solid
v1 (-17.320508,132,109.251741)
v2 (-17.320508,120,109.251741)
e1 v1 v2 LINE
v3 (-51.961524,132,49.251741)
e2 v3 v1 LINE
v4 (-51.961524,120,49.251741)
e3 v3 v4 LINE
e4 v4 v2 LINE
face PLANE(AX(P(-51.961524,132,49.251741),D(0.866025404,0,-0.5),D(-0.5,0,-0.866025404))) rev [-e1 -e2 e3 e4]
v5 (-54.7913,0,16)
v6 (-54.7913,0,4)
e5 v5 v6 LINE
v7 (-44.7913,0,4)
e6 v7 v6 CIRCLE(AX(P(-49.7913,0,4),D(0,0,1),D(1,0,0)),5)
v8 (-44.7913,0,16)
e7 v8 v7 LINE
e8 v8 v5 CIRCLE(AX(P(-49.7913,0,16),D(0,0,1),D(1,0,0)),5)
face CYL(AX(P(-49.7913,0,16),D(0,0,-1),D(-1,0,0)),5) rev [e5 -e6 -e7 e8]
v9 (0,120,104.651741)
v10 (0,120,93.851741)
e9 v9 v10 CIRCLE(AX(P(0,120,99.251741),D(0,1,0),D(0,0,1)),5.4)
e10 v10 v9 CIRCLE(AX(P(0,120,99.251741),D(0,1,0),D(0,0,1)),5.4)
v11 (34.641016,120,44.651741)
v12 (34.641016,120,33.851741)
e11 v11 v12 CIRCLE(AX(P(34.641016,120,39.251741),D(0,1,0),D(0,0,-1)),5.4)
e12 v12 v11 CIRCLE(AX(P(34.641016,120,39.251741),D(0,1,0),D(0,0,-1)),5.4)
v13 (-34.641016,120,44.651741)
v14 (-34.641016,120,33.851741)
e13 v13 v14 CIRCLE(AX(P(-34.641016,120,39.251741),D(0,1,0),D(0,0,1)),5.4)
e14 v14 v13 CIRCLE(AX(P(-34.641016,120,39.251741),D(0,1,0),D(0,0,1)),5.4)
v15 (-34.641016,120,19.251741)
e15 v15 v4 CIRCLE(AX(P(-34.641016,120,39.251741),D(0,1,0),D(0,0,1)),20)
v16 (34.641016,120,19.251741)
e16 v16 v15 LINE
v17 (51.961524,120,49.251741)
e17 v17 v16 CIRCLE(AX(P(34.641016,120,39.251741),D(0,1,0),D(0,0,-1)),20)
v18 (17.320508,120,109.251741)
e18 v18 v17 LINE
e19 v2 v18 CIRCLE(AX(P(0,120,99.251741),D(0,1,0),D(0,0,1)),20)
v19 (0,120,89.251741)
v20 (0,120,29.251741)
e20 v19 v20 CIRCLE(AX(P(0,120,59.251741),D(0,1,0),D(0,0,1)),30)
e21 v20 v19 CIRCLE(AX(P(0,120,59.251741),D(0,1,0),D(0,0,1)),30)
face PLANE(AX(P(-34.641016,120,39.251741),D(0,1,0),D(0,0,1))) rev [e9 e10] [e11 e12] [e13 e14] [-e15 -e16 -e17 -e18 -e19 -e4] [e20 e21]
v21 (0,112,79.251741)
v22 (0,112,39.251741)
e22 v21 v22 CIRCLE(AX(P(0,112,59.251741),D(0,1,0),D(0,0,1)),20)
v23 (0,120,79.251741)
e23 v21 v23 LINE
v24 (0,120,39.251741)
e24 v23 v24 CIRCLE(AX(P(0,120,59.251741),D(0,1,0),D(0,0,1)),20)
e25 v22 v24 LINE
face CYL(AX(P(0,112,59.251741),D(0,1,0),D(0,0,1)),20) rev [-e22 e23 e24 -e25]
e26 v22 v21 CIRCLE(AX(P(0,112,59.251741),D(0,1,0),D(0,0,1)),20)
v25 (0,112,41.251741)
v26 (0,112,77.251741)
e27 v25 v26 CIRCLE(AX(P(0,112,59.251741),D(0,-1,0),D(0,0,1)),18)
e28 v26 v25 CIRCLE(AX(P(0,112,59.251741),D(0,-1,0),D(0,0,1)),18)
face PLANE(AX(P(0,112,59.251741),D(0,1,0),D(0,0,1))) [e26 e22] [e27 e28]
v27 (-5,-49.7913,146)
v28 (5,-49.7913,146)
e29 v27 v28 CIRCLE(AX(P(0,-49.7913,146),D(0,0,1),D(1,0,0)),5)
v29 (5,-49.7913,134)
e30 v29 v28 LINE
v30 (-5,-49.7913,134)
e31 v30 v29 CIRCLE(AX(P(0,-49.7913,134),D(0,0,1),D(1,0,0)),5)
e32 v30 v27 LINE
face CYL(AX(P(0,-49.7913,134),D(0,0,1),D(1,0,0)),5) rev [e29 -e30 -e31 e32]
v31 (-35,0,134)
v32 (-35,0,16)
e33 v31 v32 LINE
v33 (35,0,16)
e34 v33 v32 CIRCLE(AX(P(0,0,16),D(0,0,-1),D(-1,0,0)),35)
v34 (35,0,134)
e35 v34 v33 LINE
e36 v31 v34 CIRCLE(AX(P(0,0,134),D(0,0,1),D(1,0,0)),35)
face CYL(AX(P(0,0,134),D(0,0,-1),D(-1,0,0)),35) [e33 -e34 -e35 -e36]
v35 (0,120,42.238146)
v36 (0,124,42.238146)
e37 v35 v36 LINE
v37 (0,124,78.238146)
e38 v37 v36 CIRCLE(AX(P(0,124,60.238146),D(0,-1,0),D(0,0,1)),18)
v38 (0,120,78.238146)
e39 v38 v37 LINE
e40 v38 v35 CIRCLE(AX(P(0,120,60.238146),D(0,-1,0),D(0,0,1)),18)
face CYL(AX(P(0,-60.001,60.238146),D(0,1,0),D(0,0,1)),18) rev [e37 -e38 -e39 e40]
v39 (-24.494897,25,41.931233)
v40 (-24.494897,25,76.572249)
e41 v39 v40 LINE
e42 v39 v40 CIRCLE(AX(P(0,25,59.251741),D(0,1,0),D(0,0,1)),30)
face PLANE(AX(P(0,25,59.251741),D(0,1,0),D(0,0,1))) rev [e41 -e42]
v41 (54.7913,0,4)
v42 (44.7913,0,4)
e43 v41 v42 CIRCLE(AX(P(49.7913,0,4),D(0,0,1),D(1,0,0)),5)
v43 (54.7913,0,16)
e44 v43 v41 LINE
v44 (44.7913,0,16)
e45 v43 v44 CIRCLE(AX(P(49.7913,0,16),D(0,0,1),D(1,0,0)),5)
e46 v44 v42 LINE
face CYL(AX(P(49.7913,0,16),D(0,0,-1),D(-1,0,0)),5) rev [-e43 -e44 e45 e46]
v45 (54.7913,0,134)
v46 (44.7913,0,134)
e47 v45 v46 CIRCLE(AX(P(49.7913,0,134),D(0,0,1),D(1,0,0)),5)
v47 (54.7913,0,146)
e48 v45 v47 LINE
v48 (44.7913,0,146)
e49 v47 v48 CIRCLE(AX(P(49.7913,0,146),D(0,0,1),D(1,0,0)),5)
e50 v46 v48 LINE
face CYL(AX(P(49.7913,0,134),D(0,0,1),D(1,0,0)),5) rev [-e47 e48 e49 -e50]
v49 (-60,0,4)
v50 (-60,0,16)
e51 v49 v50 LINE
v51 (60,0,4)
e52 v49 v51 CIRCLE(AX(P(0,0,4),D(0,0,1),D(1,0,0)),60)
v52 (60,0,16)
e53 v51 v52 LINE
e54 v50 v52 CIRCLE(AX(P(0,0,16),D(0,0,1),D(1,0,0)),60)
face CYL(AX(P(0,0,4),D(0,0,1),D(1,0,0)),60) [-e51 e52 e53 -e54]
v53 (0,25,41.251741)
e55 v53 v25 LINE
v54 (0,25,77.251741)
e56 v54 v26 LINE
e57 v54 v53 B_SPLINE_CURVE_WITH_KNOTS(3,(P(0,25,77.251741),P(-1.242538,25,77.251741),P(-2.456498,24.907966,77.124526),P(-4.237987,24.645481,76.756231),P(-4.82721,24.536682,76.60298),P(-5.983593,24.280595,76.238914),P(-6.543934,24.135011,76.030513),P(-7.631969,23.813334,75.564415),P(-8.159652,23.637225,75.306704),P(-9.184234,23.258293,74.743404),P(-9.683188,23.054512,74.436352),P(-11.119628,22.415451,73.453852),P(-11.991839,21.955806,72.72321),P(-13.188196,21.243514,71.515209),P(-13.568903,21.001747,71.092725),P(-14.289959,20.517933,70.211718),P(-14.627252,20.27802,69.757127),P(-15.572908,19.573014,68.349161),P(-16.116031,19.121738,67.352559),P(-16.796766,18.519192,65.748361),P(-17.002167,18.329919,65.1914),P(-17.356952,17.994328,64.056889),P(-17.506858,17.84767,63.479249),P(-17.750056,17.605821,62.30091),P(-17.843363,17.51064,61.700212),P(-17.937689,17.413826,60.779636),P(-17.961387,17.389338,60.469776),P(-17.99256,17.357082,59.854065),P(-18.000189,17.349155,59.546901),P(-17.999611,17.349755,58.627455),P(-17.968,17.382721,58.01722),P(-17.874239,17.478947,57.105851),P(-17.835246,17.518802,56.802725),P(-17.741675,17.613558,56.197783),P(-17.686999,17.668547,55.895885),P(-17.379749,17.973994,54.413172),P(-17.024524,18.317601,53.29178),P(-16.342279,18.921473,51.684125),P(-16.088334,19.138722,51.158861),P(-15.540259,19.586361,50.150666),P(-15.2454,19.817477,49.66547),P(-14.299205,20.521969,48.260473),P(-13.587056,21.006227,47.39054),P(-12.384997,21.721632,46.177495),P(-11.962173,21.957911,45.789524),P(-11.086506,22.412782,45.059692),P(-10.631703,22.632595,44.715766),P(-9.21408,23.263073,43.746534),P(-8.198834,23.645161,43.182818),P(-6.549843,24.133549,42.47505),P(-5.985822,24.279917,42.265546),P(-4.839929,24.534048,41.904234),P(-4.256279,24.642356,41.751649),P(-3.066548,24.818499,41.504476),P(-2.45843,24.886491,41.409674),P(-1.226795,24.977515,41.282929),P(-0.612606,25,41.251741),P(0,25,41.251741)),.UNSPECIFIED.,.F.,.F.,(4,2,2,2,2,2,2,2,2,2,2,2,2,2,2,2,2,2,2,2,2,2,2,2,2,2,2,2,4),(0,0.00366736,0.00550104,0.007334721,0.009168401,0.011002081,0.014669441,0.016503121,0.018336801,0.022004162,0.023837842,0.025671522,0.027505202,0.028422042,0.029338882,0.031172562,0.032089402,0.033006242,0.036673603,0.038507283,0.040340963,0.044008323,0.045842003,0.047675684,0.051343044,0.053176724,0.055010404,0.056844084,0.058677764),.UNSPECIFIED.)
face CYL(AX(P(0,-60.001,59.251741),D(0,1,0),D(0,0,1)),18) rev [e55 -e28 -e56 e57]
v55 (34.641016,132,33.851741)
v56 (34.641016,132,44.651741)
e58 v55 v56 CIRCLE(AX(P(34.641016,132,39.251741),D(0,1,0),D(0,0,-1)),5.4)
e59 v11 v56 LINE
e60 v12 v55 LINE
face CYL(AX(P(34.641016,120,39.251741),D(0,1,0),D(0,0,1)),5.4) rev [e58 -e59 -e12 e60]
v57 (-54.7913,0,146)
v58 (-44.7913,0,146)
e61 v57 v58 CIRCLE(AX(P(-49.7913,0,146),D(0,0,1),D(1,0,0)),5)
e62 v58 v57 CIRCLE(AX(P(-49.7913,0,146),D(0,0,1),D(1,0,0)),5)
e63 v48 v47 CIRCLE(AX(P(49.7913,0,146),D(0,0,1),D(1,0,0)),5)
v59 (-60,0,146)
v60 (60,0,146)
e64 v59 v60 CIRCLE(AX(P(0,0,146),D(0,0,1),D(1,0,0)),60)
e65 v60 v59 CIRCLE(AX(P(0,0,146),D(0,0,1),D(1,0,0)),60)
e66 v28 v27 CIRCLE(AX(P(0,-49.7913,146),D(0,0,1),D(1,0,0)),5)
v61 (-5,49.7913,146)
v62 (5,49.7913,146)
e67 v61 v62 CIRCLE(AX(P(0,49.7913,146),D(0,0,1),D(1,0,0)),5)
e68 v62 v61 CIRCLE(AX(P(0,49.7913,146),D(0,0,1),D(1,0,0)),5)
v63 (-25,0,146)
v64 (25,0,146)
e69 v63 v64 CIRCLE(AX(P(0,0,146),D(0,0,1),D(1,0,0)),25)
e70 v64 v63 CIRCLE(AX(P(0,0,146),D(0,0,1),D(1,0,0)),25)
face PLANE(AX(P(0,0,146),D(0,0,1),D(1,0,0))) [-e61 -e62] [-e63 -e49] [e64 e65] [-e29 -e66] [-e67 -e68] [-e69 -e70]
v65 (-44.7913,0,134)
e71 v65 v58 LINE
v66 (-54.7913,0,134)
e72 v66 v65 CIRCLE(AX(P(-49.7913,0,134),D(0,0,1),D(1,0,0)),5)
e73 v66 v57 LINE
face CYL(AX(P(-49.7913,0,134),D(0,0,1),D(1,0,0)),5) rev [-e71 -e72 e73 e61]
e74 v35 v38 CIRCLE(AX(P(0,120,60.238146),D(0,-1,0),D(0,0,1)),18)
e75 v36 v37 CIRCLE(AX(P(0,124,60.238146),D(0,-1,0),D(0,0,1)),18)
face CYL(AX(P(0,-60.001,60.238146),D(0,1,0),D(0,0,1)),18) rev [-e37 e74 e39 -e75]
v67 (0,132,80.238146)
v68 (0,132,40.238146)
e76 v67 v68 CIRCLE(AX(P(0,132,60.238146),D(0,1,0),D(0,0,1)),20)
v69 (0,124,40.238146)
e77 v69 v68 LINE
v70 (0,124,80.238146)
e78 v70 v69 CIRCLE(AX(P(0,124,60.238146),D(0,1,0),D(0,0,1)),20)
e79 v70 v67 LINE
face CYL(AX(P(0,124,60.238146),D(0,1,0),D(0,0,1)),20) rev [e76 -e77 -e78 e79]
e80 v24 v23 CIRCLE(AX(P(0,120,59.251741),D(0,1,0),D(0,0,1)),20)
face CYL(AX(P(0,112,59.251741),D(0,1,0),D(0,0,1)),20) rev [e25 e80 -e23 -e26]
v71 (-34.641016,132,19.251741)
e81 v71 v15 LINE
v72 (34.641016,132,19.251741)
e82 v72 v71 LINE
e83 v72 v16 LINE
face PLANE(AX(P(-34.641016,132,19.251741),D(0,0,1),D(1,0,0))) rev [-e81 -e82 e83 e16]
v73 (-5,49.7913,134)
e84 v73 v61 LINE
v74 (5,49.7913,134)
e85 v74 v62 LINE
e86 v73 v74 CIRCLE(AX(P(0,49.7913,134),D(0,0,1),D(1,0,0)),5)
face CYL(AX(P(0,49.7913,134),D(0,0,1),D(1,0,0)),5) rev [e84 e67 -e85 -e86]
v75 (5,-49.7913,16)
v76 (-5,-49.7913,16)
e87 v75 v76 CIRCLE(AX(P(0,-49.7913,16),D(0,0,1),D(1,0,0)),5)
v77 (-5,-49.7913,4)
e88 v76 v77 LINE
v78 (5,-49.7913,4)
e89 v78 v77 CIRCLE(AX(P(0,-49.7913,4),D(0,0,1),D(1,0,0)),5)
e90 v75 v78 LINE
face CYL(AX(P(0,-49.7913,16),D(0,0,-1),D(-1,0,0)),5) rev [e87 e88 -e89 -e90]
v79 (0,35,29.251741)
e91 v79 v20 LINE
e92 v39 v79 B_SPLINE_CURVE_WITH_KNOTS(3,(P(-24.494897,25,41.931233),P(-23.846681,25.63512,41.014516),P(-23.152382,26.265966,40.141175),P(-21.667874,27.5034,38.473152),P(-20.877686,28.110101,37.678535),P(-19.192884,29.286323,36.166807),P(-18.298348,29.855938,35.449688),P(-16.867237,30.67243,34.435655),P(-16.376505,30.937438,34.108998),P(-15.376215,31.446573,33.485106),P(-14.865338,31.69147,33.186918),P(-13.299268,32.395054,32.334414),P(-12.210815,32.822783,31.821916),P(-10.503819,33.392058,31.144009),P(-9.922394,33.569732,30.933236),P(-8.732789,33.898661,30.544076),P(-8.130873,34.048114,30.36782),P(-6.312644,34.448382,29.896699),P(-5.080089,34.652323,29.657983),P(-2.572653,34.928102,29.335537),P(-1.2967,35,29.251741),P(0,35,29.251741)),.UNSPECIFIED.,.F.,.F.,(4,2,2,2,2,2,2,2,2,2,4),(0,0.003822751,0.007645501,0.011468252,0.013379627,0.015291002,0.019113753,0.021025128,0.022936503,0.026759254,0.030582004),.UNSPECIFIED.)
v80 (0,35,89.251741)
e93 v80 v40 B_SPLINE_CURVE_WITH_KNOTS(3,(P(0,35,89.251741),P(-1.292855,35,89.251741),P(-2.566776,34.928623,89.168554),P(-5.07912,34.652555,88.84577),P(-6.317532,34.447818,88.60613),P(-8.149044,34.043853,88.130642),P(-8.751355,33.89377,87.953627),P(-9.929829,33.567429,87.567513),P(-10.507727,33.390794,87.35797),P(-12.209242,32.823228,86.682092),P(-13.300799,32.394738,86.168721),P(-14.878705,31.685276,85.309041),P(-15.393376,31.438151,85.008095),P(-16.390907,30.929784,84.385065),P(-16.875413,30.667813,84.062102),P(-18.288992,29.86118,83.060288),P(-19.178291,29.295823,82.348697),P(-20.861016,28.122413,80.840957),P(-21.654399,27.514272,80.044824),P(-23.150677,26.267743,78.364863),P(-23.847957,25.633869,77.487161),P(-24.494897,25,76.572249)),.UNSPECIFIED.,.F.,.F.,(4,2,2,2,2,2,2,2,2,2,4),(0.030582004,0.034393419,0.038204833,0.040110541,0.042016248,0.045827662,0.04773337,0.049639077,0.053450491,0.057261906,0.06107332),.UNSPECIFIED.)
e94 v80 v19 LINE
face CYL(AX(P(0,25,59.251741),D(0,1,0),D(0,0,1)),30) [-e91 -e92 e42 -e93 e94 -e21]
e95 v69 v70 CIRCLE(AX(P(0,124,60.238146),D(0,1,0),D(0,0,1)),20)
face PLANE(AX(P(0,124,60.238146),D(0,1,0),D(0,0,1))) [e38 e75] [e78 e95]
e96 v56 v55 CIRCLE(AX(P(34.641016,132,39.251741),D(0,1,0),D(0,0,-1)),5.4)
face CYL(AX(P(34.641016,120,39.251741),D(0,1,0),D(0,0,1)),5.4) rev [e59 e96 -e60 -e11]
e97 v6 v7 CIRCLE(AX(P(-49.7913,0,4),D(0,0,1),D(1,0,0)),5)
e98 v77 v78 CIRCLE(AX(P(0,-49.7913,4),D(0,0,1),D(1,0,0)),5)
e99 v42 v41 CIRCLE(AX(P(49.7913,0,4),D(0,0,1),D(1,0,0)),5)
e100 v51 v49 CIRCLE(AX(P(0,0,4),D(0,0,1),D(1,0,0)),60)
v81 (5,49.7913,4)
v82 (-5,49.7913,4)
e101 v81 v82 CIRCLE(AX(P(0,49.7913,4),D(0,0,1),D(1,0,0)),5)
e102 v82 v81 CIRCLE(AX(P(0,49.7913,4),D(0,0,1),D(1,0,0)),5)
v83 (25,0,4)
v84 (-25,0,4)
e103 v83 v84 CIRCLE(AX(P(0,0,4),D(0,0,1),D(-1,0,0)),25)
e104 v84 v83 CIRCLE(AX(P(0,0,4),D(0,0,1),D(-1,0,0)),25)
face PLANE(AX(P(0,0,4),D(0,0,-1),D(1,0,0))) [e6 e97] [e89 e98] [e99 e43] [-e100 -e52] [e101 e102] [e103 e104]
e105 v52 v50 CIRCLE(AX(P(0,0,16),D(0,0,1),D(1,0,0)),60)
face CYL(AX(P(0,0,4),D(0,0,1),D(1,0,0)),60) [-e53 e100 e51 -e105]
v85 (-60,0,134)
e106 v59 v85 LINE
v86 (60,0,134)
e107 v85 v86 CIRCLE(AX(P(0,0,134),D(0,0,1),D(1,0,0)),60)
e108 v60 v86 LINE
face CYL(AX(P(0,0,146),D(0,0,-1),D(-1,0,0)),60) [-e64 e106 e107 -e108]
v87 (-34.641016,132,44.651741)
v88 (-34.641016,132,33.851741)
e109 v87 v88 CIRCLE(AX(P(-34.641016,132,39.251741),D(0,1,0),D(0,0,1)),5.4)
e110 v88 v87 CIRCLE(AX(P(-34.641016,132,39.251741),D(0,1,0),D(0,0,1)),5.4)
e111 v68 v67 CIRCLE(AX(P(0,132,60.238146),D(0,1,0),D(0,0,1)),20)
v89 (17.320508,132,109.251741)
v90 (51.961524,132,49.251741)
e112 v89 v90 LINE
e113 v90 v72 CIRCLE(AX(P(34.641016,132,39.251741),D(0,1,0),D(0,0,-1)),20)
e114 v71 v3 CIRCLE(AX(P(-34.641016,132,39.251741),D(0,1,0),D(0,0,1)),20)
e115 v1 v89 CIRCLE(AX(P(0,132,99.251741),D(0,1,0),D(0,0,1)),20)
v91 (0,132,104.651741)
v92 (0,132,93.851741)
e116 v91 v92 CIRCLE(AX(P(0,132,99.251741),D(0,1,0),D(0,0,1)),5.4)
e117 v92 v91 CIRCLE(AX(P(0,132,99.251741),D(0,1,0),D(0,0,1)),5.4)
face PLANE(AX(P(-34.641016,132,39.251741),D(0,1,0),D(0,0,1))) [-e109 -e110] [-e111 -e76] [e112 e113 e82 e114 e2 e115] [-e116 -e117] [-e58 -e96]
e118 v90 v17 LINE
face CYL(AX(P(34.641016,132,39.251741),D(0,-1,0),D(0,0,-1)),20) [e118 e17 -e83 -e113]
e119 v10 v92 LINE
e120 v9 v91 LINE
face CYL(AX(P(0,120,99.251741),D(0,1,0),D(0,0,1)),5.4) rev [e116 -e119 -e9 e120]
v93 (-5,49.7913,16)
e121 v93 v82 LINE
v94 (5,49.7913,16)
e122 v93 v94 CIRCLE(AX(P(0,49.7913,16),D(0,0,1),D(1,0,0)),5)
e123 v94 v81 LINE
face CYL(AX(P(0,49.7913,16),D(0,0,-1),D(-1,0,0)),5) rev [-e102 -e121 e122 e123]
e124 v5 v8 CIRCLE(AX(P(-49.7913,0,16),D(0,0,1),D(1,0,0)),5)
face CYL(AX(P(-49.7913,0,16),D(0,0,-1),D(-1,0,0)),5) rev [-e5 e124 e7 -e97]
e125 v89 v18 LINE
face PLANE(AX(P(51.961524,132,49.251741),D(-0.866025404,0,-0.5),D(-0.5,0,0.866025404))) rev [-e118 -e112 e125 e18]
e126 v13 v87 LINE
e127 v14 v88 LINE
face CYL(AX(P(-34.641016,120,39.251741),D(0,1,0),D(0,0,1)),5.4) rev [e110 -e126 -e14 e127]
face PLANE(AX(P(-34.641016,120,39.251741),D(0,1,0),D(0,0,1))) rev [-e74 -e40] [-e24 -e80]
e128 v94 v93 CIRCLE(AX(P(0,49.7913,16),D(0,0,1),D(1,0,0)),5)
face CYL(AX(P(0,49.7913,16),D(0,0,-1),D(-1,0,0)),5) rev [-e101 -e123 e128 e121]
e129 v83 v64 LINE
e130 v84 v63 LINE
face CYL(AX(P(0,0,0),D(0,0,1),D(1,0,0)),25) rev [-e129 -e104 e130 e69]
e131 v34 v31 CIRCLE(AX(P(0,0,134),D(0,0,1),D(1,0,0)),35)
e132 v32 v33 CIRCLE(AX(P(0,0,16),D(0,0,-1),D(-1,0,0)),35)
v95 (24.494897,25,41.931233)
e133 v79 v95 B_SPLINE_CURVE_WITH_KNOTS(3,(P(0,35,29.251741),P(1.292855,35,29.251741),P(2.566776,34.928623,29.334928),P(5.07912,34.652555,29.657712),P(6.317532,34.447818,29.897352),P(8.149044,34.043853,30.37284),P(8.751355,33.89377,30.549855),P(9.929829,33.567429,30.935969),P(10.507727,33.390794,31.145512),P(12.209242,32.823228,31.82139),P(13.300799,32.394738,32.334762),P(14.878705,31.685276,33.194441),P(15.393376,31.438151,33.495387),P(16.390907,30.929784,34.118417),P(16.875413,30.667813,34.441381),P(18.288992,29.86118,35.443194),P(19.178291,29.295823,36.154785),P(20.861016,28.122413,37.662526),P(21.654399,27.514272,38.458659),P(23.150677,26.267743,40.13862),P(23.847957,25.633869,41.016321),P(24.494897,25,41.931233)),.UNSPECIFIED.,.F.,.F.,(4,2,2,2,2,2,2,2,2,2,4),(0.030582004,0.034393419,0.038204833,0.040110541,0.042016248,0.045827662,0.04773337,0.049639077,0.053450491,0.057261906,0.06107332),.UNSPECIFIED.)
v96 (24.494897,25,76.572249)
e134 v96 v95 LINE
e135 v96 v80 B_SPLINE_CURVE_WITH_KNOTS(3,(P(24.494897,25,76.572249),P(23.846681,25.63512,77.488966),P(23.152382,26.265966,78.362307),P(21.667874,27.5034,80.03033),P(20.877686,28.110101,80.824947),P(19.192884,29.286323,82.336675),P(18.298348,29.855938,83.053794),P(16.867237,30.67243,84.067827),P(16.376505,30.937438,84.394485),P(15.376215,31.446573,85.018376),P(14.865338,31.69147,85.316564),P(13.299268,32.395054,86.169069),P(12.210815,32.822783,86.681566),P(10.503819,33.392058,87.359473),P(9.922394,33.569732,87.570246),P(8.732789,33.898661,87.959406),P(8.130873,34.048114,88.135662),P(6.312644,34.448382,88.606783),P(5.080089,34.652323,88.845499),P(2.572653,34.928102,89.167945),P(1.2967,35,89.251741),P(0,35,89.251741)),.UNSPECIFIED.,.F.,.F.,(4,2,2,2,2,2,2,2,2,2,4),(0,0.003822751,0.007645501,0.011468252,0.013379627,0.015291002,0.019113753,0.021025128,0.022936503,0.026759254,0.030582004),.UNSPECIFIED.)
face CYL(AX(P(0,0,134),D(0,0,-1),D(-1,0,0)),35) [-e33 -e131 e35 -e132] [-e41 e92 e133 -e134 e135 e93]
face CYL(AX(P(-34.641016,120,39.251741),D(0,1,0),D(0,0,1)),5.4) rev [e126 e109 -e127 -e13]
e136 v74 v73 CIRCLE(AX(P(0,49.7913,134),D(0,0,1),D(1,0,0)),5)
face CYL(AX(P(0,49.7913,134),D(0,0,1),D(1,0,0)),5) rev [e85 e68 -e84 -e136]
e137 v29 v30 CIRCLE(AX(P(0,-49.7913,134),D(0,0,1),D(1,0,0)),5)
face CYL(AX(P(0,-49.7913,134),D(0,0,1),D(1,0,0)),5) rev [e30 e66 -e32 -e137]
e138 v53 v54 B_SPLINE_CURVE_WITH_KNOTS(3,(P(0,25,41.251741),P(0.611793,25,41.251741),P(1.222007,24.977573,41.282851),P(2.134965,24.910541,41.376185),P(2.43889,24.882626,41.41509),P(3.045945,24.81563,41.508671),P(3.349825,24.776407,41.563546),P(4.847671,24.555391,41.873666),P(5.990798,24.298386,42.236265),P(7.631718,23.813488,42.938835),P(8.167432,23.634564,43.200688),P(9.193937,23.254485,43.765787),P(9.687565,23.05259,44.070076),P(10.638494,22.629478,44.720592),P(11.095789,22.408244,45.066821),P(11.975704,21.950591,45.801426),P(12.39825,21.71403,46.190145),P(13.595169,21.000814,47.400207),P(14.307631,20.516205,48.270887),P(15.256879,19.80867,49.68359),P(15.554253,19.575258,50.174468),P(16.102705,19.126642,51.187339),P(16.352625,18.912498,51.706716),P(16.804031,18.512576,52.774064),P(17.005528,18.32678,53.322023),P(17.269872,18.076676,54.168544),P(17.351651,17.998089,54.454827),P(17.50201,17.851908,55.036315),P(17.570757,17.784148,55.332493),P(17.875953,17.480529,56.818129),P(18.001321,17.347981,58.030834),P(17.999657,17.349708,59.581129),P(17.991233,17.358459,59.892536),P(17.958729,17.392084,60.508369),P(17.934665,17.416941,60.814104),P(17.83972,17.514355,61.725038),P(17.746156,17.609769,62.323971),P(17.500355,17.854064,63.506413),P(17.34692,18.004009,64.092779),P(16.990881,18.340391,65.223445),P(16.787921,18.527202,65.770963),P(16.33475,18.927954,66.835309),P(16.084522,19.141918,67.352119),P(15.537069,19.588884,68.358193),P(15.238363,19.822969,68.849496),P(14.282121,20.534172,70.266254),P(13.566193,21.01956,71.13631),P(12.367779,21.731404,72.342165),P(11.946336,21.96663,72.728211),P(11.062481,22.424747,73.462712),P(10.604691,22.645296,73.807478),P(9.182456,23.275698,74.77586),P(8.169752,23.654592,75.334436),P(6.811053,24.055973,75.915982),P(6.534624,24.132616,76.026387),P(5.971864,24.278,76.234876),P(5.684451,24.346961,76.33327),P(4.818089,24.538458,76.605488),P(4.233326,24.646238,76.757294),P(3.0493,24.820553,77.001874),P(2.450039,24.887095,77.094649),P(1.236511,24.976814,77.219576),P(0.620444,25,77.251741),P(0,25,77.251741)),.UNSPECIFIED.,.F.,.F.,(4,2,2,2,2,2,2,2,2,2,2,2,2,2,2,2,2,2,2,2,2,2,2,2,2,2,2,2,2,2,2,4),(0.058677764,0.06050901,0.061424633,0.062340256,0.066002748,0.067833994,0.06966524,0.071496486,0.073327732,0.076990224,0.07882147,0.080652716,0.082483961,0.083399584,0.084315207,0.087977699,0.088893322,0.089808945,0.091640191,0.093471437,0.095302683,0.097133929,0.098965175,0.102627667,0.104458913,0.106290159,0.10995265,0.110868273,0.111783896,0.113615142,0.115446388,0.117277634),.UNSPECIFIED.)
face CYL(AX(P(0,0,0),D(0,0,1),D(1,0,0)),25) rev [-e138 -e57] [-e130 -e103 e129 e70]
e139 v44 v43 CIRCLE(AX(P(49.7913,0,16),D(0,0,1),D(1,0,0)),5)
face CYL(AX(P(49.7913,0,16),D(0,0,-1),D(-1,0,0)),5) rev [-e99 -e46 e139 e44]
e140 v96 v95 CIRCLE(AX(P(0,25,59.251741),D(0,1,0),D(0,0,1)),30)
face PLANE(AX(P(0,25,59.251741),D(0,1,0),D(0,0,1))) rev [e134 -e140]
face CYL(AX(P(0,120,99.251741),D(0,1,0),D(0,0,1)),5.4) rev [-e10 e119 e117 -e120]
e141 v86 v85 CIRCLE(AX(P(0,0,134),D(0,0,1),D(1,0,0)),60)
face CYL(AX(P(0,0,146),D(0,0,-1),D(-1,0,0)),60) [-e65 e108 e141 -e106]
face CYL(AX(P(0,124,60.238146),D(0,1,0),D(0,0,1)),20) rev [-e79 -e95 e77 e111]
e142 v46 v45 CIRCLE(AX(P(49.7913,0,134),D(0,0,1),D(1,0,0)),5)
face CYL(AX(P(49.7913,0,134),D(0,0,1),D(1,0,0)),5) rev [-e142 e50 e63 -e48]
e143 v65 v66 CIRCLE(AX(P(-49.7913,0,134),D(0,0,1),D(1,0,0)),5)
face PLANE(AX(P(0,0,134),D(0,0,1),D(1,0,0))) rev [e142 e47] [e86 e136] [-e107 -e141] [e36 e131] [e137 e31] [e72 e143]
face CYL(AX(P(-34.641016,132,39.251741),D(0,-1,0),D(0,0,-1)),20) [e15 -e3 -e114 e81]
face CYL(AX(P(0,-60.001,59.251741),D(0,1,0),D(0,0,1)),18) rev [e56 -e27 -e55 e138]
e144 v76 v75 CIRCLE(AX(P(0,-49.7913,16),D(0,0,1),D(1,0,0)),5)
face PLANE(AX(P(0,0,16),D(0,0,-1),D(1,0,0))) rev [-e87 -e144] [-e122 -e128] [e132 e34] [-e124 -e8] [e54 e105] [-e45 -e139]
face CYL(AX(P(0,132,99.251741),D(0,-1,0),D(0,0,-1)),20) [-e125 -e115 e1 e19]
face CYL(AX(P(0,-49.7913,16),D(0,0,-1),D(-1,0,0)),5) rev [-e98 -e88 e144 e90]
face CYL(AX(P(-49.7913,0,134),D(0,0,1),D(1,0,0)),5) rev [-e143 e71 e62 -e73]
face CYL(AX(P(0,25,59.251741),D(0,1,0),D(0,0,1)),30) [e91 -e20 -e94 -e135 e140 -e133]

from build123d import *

# Parameters (mm, degrees)
MAIN_PIPE_SKETCH_R                   = 35
MAIN_PIPE_70X134_DEPTH               = 134
MAIN_BORE_SKETCH_R                   = 25
MAIN_BORE_50_DEPTH                   = 134
END_FLANGE_SKETCH_R                  = 60
END_FLANGE_120X12_DEPTH              = 12
END_FLANGE_BOLT_HOLES_SKETCH_R       = 5
END_FLANGE_BOLT_HOLES_4X_10_DEPTH    = 12
END_FLANGE_BORE_SKETCH_R             = 25
END_FLANGE_BORE_50_DEPTH             = 169.866811422
OPPOSITE_FLANGE_BORE_SKETCH_R        = 25
OPPOSITE_FLANGE_BORE_DEPTH           = 166.420675854
END_FACE_CUT_SKETCH_R                = 35
END_FACE_CUT_4MM_DEPTH               = 4
BRANCH_PIPE_SKETCH_R                 = 30
BRANCH_PIPE_60_DEPTH                 = 95
BRANCH_BORE_36_REACH                 = 241.408
BRANCH_BORE_36_END_RADIUS            = 25
BRANCH_BORE_SKETCH_R                 = 18
BRANCH_COUNTERBORE_SKETCH_R          = 20
BRANCH_COUNTERBORE_40X8_DEPTH        = 8
TRIANGULAR_BRANCH_FLANGE_DEPTH       = 12
BRANCH_FLANGE_HOLES_SKETCH_R         = 5.4
BRANCH_FLANGE_BOLT_HOLES_DEPTH       = 12
BRANCH_FLANGE_BORE_36_REACH          = 250.556
BRANCH_FLANGE_BORE_SKETCH_R          = 18
BRANCH_FLANGE_COUNTERBORE_SKETCH_R   = 20
BRANCH_FLANGE_COUNTERBORE_40X8_DEPTH = 8


with BuildPart() as part:
    # Main Pipe Sketch → Main Pipe Ø70x134 (new body)
    with BuildSketch(Plane.XY):
        Circle(MAIN_PIPE_SKETCH_R)
    extrude(amount=MAIN_PIPE_70X134_DEPTH)

    # Main Bore Sketch → Main Bore Ø50 (cut)
    with BuildSketch(Plane.XY.offset(134)):
        Circle(MAIN_BORE_SKETCH_R)
    extrude(amount=-MAIN_BORE_50_DEPTH, mode=Mode.SUBTRACT)

    # End Flange Sketch → End Flange Ø120x12 (add)
    with BuildSketch(Plane.XY.offset(134)):
        Circle(END_FLANGE_SKETCH_R)
    end_flange_120x12 = extrude(amount=END_FLANGE_120X12_DEPTH)

    # End Flange Bolt Holes Sketch → End Flange Bolt Holes 4xØ10 (cut)
    with BuildSketch(Plane.XY.offset(146)):
        with Locations((0, 49.791299633)):
            Circle(END_FLANGE_BOLT_HOLES_SKETCH_R)
        with Locations((49.791299633, 0)):
            Circle(END_FLANGE_BOLT_HOLES_SKETCH_R)
        with Locations((0, -49.791299633)):
            Circle(END_FLANGE_BOLT_HOLES_SKETCH_R)
        with Locations((-49.791299633, 0)):
            Circle(END_FLANGE_BOLT_HOLES_SKETCH_R)
    end_flange_bolt_holes_4x_10 = extrude(amount=-END_FLANGE_BOLT_HOLES_4X_10_DEPTH, mode=Mode.SUBTRACT)

    # End Flange Bore Sketch → End Flange Bore Ø50 (cut, through all)
    with BuildSketch(Plane.XY.offset(146)):
        Circle(END_FLANGE_BORE_SKETCH_R)
    extrude(amount=-END_FLANGE_BORE_50_DEPTH, mode=Mode.SUBTRACT)

    # Opposite End Flange Mirror: End Flange Ø120x12, End Flange Bolt Holes 4xØ10 across plane
    add(end_flange_120x12.mirror(Plane.XY.offset(75)))
    add(end_flange_bolt_holes_4x_10.mirror(Plane.XY.offset(75)), mode=Mode.SUBTRACT)

    # Opposite Flange Bore Sketch → Opposite Flange Bore (cut, through all)
    with BuildSketch(Plane(origin=(0, 0, 4), x_dir=(-1, 0, 0), z_dir=(0, 0, -1))):
        with Locations(Location((0, 0, 0), (0, 0, 180))):
            Circle(OPPOSITE_FLANGE_BORE_SKETCH_R)
    extrude(amount=-OPPOSITE_FLANGE_BORE_DEPTH, mode=Mode.SUBTRACT)

    # End Face Cut Sketch → End Face Cut 4mm (cut)
    with BuildSketch(Plane(origin=(0, 0, 0), x_dir=(-1, 0, 0), z_dir=(0, 0, -1))):
        Circle(END_FACE_CUT_SKETCH_R)
    extrude(amount=-END_FACE_CUT_4MM_DEPTH, mode=Mode.SUBTRACT)

    # Branch Pipe Sketch → Branch Pipe Ø60 (add)
    with BuildSketch(Plane(origin=(0, 120, 0), x_dir=(1, 0, 0), z_dir=(0, 1, 0))):
        with Locations(Location((0, -59.251741082, 0), (0, 0, 270))):
            Circle(BRANCH_PIPE_SKETCH_R)
    extrude(amount=-BRANCH_PIPE_60_DEPTH)

    # Branch Bore Ø36: up to this cylinder (the profile starts outside it)
    branch_bore_36_end = Plane(origin=(0, 0, 59.251741), z_dir=(0, 0, 1)) * Cylinder(BRANCH_BORE_36_END_RADIUS, 533.816, mode=Mode.PRIVATE)
    # Branch Bore Sketch → Branch Bore Ø36 (cut, up to the surface)
    with BuildSketch(Plane(origin=(0, 120, 0), x_dir=(1, 0, 0), z_dir=(0, 1, 0)), mode=Mode.PRIVATE) as branch_bore_36_sk1:
        with Locations(Location((0, -59.251741082, 0), (0, 0, 270))):
            Circle(BRANCH_BORE_SKETCH_R)
    branch_bore_36_tool1 = extrude(branch_bore_36_sk1.sketch, amount=-BRANCH_BORE_36_REACH, mode=Mode.PRIVATE) - branch_bore_36_end
    add(branch_bore_36_tool1.solids().sort_by_distance((0, 120, 59.251741))[0], mode=Mode.SUBTRACT)

    # Branch Counterbore Sketch → Branch Counterbore Ø40x8 (cut)
    with BuildSketch(Plane(origin=(0, 120, 0), x_dir=(1, 0, 0), z_dir=(0, 1, 0))):
        with Locations(Location((0, -59.251741082, 0), (0, 0, 270))):
            Circle(BRANCH_COUNTERBORE_SKETCH_R)
    extrude(amount=-BRANCH_COUNTERBORE_40X8_DEPTH, mode=Mode.SUBTRACT)

    # Branch Flange Sketch → Triangular Branch Flange (add)
    with BuildSketch(Plane(origin=(0, 120, 0), x_dir=(1, 0, 0), z_dir=(0, 1, 0))):
        with BuildLine():
            Line((-51.961524227, -49.251741082), (-17.320508076, -109.251741082))
            ThreePointArc((-17.320508076, -109.251741082), (0, -119.251741082), (17.320508076, -109.251741082))
            Line((17.320508076, -109.251741082), (51.961524227, -49.251741082))
            ThreePointArc((51.961524227, -49.251741082), (51.961524227, -29.251741082), (34.641016151, -19.251741082))
            Line((34.641016151, -19.251741082), (-34.641016151, -19.251741082))
            ThreePointArc((-34.641016151, -19.251741082), (-51.961524227, -29.251741082), (-51.961524227, -49.251741082))
        make_face()
    extrude(amount=TRIANGULAR_BRANCH_FLANGE_DEPTH)

    # Branch Flange Holes Sketch → Branch Flange Bolt Holes (cut)
    with BuildSketch(Plane(origin=(0, 132, 0), x_dir=(1, 0, 0), z_dir=(0, 1, 0))):
        with Locations(Location((-34.641016151, -39.251741082, 0), (0, 0, 270))):
            Circle(BRANCH_FLANGE_HOLES_SKETCH_R)
        with Locations(Location((34.641016151, -39.251741082, 0), (0, 0, 90))):
            Circle(BRANCH_FLANGE_HOLES_SKETCH_R)
        with Locations(Location((0, -99.251741082, 0), (0, 0, 270))):
            Circle(BRANCH_FLANGE_HOLES_SKETCH_R)
    extrude(amount=-BRANCH_FLANGE_BOLT_HOLES_DEPTH, mode=Mode.SUBTRACT)

    # Branch Flange Bore Sketch → Branch Flange Bore Ø36 (cut, up to next)
    with BuildSketch(Plane(origin=(0, 132, 0), x_dir=(1, 0, 0), z_dir=(0, 1, 0)), mode=Mode.PRIVATE) as branch_flange_bore_36_sk1:
        with Locations(Location((0, -60.238145752, 0), (0, 0, 270))):
            Circle(BRANCH_FLANGE_BORE_SKETCH_R)
    branch_flange_bore_36_tool1 = extrude(branch_flange_bore_36_sk1.sketch, amount=-BRANCH_FLANGE_BORE_36_REACH, mode=Mode.PRIVATE) & part.part
    add(branch_flange_bore_36_tool1.solids().sort_by_distance((0, 132, 60.238146))[0], mode=Mode.SUBTRACT)

    # Branch Flange Counterbore Sketch → Branch Flange Counterbore Ø40x8 (cut)
    with BuildSketch(Plane(origin=(0, 132, 0), x_dir=(1, 0, 0), z_dir=(0, 1, 0))):
        with Locations(Location((0, -60.238145752, 0), (0, 0, 270))):
            Circle(BRANCH_FLANGE_COUNTERBORE_SKETCH_R)
    extrude(amount=-BRANCH_FLANGE_COUNTERBORE_40X8_DEPTH, mode=Mode.SUBTRACT)


solid = part.part
